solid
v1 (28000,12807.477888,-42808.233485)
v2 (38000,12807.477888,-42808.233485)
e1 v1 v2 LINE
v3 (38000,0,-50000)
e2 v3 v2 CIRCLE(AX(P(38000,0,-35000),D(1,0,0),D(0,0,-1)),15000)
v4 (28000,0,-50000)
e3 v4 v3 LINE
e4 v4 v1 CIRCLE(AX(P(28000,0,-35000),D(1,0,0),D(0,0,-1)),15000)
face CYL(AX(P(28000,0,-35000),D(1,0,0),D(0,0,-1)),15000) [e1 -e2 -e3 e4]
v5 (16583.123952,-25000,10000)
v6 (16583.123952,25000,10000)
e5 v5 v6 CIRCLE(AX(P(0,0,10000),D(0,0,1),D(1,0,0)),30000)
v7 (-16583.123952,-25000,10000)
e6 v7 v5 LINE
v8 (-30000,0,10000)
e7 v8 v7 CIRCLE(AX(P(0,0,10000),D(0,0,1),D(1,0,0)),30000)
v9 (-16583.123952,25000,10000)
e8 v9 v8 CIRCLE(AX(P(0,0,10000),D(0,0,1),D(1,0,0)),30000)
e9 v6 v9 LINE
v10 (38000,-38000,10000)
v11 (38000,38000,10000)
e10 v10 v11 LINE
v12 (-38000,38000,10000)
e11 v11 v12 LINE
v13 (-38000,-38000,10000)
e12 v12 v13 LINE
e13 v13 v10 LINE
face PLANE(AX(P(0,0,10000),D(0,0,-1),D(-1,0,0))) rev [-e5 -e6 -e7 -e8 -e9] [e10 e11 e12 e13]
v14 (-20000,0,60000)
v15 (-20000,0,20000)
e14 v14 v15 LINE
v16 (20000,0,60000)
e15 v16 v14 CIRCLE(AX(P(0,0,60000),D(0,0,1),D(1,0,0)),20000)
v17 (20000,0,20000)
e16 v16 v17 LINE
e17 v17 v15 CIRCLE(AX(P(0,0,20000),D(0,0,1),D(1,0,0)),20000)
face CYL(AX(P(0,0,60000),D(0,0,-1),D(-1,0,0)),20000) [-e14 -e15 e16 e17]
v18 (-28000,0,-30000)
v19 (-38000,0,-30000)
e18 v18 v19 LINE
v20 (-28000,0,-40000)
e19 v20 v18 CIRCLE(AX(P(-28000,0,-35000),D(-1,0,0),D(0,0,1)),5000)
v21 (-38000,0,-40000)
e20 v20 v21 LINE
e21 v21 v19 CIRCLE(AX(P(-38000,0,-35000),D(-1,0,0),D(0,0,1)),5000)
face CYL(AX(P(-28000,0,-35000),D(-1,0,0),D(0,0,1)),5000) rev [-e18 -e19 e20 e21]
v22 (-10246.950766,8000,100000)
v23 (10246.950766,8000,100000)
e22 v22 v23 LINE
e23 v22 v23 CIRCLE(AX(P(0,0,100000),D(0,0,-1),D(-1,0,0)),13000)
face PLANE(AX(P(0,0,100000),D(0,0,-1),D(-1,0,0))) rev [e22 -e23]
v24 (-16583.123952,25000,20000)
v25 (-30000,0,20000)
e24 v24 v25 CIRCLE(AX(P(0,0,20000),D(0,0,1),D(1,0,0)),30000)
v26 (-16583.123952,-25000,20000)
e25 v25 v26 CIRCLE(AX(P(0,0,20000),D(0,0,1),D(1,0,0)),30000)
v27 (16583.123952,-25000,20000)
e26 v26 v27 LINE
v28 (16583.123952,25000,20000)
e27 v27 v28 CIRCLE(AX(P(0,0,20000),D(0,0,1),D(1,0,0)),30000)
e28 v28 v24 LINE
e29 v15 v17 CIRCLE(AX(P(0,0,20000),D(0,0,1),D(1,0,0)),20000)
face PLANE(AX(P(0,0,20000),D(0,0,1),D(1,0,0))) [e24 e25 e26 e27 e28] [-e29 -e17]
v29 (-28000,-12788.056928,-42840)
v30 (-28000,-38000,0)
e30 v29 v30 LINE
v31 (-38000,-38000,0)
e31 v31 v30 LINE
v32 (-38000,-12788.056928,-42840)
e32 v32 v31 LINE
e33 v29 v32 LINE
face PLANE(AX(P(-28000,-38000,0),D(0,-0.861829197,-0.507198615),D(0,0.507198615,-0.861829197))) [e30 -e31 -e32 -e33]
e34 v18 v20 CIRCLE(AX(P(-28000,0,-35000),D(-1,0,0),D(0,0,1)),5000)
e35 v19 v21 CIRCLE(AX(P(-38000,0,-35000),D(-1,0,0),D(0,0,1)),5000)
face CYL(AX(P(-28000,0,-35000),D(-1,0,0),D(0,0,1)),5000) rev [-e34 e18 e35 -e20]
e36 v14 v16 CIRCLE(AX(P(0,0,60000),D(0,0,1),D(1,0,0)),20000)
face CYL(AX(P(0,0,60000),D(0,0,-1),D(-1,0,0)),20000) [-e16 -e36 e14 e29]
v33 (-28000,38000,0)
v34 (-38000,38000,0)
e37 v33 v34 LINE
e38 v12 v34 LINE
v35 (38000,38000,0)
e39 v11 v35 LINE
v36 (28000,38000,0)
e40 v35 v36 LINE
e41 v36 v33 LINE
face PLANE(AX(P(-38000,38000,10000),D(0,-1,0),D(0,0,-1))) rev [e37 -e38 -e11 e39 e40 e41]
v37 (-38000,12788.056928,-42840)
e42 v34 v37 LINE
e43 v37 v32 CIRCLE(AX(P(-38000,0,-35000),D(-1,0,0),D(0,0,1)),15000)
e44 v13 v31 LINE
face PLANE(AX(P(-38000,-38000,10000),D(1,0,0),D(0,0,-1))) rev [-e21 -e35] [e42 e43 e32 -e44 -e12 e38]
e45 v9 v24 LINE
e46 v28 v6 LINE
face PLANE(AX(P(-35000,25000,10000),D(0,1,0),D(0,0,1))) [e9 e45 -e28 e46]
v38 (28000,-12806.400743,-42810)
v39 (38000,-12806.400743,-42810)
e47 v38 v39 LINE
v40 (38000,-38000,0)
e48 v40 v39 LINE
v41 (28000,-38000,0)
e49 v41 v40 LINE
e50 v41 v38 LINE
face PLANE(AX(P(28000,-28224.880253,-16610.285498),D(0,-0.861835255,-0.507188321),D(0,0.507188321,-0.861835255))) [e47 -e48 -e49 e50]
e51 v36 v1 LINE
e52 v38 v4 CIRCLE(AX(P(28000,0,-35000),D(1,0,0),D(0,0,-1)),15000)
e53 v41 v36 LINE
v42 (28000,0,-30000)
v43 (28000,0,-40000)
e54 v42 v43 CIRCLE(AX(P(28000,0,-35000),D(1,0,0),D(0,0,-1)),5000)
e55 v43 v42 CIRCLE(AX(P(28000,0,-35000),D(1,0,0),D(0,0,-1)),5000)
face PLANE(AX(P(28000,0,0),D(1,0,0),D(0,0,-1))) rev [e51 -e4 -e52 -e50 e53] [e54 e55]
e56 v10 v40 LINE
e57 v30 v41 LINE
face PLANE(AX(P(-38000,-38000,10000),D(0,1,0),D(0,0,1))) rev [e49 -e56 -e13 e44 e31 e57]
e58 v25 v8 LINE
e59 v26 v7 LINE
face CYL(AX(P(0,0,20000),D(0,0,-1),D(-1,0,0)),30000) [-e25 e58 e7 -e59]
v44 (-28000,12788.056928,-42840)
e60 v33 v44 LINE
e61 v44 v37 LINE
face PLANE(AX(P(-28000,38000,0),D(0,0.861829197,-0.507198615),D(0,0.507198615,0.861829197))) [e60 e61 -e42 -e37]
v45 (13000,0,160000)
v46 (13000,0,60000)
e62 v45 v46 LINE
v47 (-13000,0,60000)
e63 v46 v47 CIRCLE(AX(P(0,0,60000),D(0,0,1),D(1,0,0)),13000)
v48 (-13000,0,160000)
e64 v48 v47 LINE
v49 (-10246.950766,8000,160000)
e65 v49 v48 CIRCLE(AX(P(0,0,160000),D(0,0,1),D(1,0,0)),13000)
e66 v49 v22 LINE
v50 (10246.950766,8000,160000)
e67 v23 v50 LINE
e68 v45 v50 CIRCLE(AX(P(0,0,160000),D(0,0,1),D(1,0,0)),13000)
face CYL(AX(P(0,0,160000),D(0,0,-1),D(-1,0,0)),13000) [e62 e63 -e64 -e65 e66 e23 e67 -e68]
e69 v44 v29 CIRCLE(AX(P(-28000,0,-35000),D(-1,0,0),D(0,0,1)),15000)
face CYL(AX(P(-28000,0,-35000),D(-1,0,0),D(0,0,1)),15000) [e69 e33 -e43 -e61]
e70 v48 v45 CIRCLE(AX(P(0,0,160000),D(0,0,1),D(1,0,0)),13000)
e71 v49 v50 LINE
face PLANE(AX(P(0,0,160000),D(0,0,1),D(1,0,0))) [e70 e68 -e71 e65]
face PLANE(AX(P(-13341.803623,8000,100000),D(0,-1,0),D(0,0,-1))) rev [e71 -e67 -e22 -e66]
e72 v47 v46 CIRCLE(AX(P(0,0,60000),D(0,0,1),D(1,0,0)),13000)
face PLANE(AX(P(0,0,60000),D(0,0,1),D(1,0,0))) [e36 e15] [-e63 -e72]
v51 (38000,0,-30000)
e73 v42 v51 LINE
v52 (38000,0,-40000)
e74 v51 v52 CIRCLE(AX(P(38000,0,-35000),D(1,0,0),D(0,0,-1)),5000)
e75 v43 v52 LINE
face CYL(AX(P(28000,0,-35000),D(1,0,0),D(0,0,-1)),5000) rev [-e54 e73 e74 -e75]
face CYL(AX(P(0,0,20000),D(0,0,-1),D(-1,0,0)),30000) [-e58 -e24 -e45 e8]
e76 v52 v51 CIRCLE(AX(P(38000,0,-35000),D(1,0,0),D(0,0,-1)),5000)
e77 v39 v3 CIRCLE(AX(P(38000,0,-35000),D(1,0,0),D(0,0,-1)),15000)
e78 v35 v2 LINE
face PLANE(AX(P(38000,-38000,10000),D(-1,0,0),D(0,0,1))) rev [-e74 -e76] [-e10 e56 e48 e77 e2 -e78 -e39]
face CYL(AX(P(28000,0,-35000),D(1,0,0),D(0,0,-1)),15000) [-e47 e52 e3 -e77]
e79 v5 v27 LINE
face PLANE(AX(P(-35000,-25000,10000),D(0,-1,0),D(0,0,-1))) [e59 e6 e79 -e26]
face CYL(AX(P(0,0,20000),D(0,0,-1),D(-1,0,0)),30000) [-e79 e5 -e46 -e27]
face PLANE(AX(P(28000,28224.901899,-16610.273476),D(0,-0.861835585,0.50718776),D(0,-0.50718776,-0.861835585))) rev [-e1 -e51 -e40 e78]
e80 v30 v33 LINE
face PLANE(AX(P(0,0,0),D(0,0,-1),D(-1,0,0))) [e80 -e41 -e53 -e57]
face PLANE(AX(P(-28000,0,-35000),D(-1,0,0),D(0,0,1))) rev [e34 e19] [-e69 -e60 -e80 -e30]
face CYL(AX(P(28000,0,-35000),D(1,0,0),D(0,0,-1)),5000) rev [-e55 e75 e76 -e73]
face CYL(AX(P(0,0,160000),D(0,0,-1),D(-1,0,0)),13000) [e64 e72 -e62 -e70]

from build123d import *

# Parameters (mm, degrees)
BASE_PLATE_SKETCH_W               = 76000
BASE_PLATE_SKETCH_H               = 76000
BASE_PLATE_DEPTH                  = 10000
CLEVIS_LUG_A_SKETCH_R             = 5000
CLEVIS_LUG_A_DEPTH                = 10000
CLEVIS_START                      = -10000
CLEVIS_LUG_B_SKETCH_R             = 5000
CLEVIS_LUG_B_DEPTH                = 10000
COLLAR_60_SKETCH_R                = 30000
COLLAR_60_DEPTH                   = 10000
HEX_COLLAR_CUT_SKETCH_OUTSIDE_W   = 101655.07
HEX_COLLAR_CUT_SKETCH_OUTSIDE_H   = 101655.07
HEX_COLLAR_CUT_SKETCH_OUTSIDE_W_2 = 70000
HEX_COLLAR_CUT_SKETCH_OUTSIDE_H_2 = 50000
HEX_COLLAR_CUT_DEPTH              = 10000
SHAFT_SHOULDER_40_SKETCH_R        = 20000
SHAFT_SHOULDER_40_DEPTH           = 40000
SHAFT_26_SKETCH_R                 = 13000
SHAFT_26_DEPTH                    = 100000
SHAFT_FLAT_SKETCH_W               = 26683.607246268
SHAFT_FLAT_SKETCH_H               = 10033.036324596
SHAFT_FLAT_CUT_DEPTH              = 60000


with BuildPart() as part:
    # Base Plate Sketch → Base Plate (new body)
    with BuildSketch(Plane.XY):
        Rectangle(BASE_PLATE_SKETCH_W, BASE_PLATE_SKETCH_H)
    extrude(amount=BASE_PLATE_DEPTH)

    # Clevis Lug A Sketch → Clevis Lug A (add)
    with BuildSketch(Plane(origin=(38000, 0, 0), x_dir=(0, 0, -1), z_dir=(1, 0, 0))):
        with BuildLine():
            Line((42405.553807794, 13044.453717955), (0, 38000))
            Line((0, 38000), (0, -38000))
            Line((0, -38000), (42810, -12806.400743378))
            ThreePointArc((42810, -12806.400743378), (49999.999964327, 1.034506538), (42808.233485002, 12807.477887691))
            Line((42808.233485002, 12807.477887691), (42405.553807794, 13044.453717955))
        make_face()
        with Locations((35000, 0)):
            Circle(CLEVIS_LUG_A_SKETCH_R, mode=Mode.SUBTRACT)
    extrude(amount=-CLEVIS_LUG_A_DEPTH)

    # Clevis Lug B Sketch → Clevis Lug B (add)
    with BuildSketch(Plane.ZY.offset(38000).offset(CLEVIS_START)):
        with BuildLine():
            Line((0, 38000), (0, -38000))
            Line((0, -38000), (-42840, -12788.056928244))
            ThreePointArc((-42840, -12788.056928244), (-50000, 0), (-42840, 12788.056928244))
            Line((-42840, 12788.056928244), (0, 38000))
        make_face()
        with Locations(Location((-35000, 0, 0), (0, 0, 180))):
            Circle(CLEVIS_LUG_B_SKETCH_R, mode=Mode.SUBTRACT)
    extrude(amount=CLEVIS_LUG_B_DEPTH)

    # Collar Ø60 Sketch → Collar Ø60 (add)
    with BuildSketch(Plane.XY.offset(10000)):
        Circle(COLLAR_60_SKETCH_R)
    extrude(amount=COLLAR_60_DEPTH)

    # Hex Collar Cut Sketch outside → Hex Collar Cut (cut)
    with BuildSketch(Plane.XY.offset(20000)):
        Rectangle(HEX_COLLAR_CUT_SKETCH_OUTSIDE_W, HEX_COLLAR_CUT_SKETCH_OUTSIDE_H)
        Rectangle(HEX_COLLAR_CUT_SKETCH_OUTSIDE_W_2, HEX_COLLAR_CUT_SKETCH_OUTSIDE_H_2, mode=Mode.SUBTRACT)
    extrude(amount=-HEX_COLLAR_CUT_DEPTH, mode=Mode.SUBTRACT)

    # Shaft Shoulder Ø40 Sketch → Shaft Shoulder Ø40 (add)
    with BuildSketch(Plane.XY.offset(20000)):
        Circle(SHAFT_SHOULDER_40_SKETCH_R)
    extrude(amount=SHAFT_SHOULDER_40_DEPTH)

    # Shaft Ø26 Sketch → Shaft Ø26 (add)
    with BuildSketch(Plane.XY.offset(60000)):
        Circle(SHAFT_26_SKETCH_R)
    extrude(amount=SHAFT_26_DEPTH)

    # Shaft Flat Sketch → Shaft Flat Cut (cut)
    with BuildSketch(Plane.XY.offset(160000)):
        with Locations((0, 13016.518162298)):
            Rectangle(SHAFT_FLAT_SKETCH_W, SHAFT_FLAT_SKETCH_H)
    extrude(amount=-SHAFT_FLAT_CUT_DEPTH, mode=Mode.SUBTRACT)


solid = part.part
